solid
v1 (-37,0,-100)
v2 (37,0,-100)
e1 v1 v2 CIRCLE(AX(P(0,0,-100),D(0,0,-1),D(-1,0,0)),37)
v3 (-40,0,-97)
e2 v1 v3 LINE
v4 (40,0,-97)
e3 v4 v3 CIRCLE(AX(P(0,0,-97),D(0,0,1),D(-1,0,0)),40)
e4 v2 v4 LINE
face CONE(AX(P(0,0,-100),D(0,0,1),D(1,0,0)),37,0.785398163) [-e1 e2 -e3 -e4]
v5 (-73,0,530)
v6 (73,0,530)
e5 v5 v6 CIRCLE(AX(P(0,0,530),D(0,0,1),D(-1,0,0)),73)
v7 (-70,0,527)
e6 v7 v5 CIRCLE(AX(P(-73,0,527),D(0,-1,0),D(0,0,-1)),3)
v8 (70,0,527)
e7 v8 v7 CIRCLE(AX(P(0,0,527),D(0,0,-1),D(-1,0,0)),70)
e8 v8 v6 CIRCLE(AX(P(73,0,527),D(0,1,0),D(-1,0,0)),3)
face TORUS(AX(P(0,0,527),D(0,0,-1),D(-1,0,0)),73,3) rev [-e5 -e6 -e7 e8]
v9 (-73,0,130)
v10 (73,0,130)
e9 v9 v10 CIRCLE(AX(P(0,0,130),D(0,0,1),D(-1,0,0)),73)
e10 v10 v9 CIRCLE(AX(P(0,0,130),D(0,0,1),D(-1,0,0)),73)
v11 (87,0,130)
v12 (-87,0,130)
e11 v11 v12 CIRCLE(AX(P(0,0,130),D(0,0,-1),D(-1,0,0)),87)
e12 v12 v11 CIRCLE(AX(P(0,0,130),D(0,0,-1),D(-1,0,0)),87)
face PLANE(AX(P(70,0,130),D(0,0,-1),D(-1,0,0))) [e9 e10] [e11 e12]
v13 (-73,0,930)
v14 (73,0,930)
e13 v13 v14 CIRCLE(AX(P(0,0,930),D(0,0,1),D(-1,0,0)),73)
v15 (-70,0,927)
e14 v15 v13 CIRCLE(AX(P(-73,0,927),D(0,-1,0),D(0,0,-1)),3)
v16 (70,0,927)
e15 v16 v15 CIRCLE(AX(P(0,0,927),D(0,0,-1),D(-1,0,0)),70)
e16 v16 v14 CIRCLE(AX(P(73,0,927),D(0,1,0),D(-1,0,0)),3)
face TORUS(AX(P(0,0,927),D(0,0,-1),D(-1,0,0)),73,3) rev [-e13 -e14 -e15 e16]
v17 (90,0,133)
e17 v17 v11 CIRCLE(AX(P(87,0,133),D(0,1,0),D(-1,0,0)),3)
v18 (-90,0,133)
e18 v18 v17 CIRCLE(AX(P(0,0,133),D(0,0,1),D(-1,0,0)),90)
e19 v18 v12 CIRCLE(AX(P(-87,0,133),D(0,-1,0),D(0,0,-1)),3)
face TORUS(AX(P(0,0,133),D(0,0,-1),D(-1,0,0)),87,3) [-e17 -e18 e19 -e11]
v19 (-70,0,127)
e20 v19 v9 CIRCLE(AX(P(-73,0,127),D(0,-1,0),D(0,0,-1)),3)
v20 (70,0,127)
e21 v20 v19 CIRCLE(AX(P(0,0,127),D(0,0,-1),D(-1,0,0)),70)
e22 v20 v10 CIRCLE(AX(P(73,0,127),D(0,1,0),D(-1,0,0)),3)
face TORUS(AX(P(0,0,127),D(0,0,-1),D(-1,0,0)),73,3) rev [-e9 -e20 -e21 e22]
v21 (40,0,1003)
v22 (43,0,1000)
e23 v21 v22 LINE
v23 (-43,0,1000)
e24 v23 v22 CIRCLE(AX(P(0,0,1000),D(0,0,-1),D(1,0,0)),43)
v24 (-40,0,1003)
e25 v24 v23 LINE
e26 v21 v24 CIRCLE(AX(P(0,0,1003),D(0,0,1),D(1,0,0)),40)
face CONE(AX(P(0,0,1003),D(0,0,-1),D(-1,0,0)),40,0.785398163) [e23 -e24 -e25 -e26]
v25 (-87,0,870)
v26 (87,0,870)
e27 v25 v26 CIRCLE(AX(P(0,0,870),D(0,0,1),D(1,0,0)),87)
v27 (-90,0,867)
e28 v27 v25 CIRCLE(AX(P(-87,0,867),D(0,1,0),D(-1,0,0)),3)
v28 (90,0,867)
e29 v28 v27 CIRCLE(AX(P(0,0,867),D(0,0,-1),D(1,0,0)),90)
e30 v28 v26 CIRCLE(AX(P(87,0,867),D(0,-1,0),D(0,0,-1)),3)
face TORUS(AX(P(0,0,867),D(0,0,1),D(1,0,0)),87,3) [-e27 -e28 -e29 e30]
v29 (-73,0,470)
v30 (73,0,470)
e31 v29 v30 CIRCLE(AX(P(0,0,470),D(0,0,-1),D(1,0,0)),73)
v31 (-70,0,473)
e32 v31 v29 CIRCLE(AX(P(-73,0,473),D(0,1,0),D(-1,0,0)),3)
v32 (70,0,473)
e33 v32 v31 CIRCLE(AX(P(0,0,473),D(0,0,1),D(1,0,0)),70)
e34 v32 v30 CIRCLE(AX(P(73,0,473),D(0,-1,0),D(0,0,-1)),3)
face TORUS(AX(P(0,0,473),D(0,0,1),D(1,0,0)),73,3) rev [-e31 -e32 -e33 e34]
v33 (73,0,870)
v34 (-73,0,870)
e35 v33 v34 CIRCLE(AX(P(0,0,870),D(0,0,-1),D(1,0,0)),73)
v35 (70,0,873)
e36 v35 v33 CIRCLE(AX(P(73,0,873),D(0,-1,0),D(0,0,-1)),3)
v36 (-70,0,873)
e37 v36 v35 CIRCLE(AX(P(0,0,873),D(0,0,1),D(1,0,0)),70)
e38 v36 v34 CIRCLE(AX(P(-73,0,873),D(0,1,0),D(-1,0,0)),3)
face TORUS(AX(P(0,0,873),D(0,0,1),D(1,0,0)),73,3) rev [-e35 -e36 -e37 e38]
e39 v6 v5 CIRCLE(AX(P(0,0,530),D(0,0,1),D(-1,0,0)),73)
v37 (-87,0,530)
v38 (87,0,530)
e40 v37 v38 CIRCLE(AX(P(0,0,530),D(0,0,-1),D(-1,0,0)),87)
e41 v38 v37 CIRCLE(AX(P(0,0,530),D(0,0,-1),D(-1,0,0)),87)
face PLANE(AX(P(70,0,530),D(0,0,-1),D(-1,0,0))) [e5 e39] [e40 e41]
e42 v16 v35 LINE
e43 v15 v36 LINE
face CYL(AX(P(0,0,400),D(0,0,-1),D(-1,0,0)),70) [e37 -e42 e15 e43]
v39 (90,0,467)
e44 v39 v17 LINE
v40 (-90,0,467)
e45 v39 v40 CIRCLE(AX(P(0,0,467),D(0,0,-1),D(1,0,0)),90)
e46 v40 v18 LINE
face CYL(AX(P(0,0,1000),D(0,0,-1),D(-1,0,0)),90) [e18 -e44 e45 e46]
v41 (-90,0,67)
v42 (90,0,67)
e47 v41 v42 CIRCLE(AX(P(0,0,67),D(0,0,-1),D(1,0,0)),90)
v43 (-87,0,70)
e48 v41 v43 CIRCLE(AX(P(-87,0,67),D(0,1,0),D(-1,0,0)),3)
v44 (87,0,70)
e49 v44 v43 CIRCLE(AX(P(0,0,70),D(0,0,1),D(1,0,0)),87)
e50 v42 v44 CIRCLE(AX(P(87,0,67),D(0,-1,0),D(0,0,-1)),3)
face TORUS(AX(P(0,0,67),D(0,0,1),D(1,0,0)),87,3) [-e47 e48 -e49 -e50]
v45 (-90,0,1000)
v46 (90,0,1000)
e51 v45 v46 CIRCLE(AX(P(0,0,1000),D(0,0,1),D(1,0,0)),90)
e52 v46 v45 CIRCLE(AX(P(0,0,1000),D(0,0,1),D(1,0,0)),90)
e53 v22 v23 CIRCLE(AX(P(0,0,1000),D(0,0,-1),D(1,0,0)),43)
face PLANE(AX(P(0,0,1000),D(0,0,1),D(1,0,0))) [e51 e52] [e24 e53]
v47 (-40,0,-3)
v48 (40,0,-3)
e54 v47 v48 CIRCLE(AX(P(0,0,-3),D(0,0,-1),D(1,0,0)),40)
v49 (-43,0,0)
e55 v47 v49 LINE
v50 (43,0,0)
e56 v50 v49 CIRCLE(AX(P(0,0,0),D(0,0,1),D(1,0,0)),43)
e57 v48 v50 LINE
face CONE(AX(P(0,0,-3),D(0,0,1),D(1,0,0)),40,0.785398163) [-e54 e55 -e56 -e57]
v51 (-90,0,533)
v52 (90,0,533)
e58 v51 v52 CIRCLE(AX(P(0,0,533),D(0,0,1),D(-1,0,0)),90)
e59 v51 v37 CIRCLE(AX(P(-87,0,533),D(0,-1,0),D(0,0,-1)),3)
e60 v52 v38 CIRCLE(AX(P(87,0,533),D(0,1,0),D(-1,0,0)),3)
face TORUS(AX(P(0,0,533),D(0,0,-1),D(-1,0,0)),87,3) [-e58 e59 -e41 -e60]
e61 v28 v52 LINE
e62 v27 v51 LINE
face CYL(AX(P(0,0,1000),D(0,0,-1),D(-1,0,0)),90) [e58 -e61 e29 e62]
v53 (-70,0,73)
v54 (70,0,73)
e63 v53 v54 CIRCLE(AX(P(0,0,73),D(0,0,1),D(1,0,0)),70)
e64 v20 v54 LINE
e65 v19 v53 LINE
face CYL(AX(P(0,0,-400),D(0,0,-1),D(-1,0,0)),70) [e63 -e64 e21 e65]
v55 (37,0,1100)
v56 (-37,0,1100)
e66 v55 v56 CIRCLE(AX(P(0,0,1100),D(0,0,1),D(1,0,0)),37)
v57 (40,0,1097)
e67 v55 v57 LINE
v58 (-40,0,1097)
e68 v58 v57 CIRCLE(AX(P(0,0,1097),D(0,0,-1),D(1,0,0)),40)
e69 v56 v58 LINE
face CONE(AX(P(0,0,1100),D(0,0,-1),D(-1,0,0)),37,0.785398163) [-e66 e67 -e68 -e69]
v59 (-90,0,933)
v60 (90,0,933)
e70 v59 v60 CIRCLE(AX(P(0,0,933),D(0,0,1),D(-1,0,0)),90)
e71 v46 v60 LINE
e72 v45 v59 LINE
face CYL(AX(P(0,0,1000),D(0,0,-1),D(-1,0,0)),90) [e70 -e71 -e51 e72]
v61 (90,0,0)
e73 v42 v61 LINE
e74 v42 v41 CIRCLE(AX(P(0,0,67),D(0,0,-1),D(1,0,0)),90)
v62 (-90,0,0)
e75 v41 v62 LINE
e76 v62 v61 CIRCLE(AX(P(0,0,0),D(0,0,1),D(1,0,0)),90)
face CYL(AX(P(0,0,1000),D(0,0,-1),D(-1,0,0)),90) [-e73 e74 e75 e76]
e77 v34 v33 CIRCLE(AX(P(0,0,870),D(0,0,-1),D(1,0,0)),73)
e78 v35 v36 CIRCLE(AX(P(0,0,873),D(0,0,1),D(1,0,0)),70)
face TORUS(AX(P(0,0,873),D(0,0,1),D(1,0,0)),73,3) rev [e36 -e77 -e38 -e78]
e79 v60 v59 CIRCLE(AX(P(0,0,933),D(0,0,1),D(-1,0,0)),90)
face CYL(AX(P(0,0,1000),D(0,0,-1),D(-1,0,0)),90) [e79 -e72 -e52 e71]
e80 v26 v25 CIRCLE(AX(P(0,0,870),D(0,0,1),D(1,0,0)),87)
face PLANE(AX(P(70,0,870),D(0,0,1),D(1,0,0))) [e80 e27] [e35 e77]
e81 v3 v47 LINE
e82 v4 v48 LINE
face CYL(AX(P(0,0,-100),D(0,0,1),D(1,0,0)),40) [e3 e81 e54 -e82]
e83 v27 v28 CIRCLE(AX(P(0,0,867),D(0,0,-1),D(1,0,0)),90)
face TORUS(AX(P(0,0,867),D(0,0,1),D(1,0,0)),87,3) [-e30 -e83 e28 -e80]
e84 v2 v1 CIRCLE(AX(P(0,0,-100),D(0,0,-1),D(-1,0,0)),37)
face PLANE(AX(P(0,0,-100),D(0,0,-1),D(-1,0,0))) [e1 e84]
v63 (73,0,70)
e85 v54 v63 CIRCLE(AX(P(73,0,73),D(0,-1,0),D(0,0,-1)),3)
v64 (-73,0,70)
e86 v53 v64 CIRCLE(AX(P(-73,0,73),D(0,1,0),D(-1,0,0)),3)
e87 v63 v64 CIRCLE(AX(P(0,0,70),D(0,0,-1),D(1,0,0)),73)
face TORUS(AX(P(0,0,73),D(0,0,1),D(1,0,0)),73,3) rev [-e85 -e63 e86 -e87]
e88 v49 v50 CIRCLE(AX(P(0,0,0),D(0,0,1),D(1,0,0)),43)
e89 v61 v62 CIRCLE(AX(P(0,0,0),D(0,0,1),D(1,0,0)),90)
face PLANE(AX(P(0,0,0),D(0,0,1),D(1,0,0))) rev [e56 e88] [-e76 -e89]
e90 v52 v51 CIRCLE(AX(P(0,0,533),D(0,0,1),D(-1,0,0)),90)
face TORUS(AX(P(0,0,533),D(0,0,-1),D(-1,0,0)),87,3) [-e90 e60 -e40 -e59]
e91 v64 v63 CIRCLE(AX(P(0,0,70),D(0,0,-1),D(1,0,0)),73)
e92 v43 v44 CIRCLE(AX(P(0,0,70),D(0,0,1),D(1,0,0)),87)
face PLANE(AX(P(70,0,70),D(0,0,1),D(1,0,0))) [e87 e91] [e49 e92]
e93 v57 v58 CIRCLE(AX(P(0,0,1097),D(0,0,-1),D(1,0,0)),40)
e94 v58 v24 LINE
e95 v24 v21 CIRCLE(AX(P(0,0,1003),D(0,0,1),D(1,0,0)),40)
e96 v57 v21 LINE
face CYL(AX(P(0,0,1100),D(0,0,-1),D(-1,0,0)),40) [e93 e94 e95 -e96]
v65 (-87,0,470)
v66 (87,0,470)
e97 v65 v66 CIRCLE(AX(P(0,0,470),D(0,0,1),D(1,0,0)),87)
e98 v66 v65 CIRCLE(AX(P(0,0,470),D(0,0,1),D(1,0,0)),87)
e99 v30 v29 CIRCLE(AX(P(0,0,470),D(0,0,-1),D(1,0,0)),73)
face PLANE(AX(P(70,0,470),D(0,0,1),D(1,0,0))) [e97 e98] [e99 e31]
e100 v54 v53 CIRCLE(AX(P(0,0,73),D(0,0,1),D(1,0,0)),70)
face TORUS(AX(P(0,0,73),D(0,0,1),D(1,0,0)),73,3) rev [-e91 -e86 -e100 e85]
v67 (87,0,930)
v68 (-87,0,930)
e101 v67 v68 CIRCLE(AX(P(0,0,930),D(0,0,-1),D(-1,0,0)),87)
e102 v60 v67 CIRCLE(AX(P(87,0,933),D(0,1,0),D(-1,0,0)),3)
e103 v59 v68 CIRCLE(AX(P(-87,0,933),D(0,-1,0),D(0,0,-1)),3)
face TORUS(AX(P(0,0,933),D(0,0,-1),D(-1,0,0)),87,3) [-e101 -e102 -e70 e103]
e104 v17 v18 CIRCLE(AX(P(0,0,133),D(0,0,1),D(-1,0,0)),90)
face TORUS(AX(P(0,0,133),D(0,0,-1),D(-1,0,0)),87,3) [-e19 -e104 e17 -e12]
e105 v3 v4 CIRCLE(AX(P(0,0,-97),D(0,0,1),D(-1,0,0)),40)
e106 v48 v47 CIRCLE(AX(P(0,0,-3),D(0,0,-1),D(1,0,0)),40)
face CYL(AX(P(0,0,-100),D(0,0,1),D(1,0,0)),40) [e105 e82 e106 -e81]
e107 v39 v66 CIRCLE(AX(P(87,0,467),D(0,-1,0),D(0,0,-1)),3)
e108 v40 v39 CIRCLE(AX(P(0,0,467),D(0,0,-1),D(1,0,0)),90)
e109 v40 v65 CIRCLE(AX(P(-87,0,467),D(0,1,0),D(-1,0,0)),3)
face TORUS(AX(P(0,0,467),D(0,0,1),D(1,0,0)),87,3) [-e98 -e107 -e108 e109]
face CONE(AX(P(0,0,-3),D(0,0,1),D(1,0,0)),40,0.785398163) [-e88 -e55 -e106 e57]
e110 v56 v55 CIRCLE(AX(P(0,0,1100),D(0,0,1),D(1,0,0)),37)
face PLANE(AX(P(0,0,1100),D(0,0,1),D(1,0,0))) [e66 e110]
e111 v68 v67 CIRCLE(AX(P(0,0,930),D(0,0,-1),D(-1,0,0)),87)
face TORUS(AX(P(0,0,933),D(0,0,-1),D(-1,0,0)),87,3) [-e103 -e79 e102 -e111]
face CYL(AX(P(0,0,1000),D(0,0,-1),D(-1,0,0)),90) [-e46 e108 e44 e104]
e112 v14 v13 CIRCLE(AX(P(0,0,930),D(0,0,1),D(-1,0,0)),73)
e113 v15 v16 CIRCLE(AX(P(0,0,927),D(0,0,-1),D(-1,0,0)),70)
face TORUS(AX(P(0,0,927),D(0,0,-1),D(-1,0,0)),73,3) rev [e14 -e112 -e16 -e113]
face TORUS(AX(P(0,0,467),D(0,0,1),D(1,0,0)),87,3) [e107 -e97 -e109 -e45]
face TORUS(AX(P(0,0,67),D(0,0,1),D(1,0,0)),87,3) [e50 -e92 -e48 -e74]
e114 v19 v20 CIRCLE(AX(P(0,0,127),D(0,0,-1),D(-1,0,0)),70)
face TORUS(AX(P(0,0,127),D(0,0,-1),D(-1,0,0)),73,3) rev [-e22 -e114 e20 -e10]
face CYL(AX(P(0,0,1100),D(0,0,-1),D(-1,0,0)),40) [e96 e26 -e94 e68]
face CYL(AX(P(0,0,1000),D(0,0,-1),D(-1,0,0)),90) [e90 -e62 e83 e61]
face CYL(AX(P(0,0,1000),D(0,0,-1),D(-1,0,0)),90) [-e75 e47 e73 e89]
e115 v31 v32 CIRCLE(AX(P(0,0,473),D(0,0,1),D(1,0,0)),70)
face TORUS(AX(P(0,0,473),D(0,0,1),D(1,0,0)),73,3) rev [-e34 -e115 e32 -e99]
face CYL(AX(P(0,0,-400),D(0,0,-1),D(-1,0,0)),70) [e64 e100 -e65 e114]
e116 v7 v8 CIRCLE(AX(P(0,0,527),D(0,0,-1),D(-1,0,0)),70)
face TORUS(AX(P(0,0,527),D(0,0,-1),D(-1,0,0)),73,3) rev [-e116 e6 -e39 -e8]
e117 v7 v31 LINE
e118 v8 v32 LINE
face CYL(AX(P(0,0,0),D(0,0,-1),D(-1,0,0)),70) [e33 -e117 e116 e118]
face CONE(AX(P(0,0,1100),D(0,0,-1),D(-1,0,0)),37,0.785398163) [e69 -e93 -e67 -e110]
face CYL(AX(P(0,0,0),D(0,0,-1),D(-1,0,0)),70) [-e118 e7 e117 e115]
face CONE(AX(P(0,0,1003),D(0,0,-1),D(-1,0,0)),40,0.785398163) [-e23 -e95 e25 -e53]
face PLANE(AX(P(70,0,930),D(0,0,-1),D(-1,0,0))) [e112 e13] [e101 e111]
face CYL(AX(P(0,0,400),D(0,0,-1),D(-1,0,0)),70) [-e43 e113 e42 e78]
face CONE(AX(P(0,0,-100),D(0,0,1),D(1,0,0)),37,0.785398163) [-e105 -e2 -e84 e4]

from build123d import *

# Parameters (mm, degrees)
SKETCH1_R                  = 90
BOSS_EXTRUDE1_DEPTH        = 1000
SKETCH2_W                  = 40
SKETCH2_H                  = 60
FILLET1_R                  = 3
LPATTERN1_COUNT            = 2
LPATTERN1_PITCH            = 400
FILLET1_OF_LPATTERN1_R     = 3
LPATTERN1_COL_COUNT        = 2
LPATTERN1_COL_PITCH        = 400
FILLET1_OF_LPATTERN1_COL_R = 3
SKETCH3_R                  = 40
BOSS_EXTRUDE2_DEPTH        = 100
CHAMFER1_SIZE              = 3
BOSS_EXTRUDE3_START        = 100
SKETCH4_R                  = 40
BOSS_EXTRUDE3_DEPTH        = 100
CHAMFER2_SIZE              = 3


with BuildPart() as part:
    # Sketch1 → Boss-Extrude1 (new body)
    with BuildSketch(Plane.XY):
        Circle(SKETCH1_R)
    extrude(amount=BOSS_EXTRUDE1_DEPTH)

    # Sketch2 → Cut-Revolve1 (revolve, cut)
    with BuildSketch(Plane(origin=(0, 0, 0), x_dir=(1, 0, 0), z_dir=(0, 1, 0)), mode=Mode.PRIVATE) as cut_revolve1_sk:
        with Locations((90, -500)):
            Rectangle(SKETCH2_W, SKETCH2_H)
    cut_revolve1 = revolve(cut_revolve1_sk.sketch.rotate(Axis((0, 0, 0), (0, 0, 1)), 180), axis=Axis((0, 0, 0), (0, 0, 1)), mode=Mode.SUBTRACT)

    # Fillet1
    fillet1_edges = [part.edges().sort_by_distance(p)[0] for p in [
        (70, 0, 530),
        (-90, 0, 530),
        (70, 0, 470),
        (-90, 0, 470),
    ]]
    fillet(fillet1_edges, radius=FILLET1_R)

    # LPattern1: Cut-Revolve1 ×2
    with Locations(*[(0, 0, -i * LPATTERN1_PITCH) for i in range(1, LPATTERN1_COUNT)]):
        add(cut_revolve1, mode=Mode.SUBTRACT)

    # Fillet1 of LPattern1
    fillet1_of_lpattern1_edges = [part.edges().sort_by_distance(p)[0] for p in [
        (70, 0, 130),
        (-90, 0, 130),
        (70, 0, 70),
        (-90, 0, 70),
    ]]
    fillet(fillet1_of_lpattern1_edges, radius=FILLET1_OF_LPATTERN1_R)

    # LPattern1 col: Cut-Revolve1 ×2
    with Locations(*[(0, 0, i * LPATTERN1_COL_PITCH) for i in range(1, LPATTERN1_COL_COUNT)]):
        add(cut_revolve1, mode=Mode.SUBTRACT)

    # Fillet1 of LPattern1 col
    fillet1_of_lpattern1_col_edges = [part.edges().sort_by_distance(p)[0] for p in [
        (70, 0, 930),
        (-90, 0, 930),
        (70, 0, 870),
        (-90, 0, 870),
    ]]
    fillet(fillet1_of_lpattern1_col_edges, radius=FILLET1_OF_LPATTERN1_COL_R)

    # Sketch3 → Boss-Extrude2 (add)
    with BuildSketch(Plane.XY.offset(1000)):
        Circle(SKETCH3_R)
    extrude(amount=BOSS_EXTRUDE2_DEPTH)

    # Chamfer1
    chamfer1_edges = [part.edges().sort_by_distance(p)[0] for p in [
        (-40, 0, 1000),
        (-40, 0, 1100),
    ]]
    chamfer(chamfer1_edges, length=CHAMFER1_SIZE)

    # Sketch4 → Boss-Extrude3 (add)
    with BuildSketch(Plane(origin=(0, 0, 0), x_dir=(-1, 0, 0), z_dir=(0, 0, -1)).offset(BOSS_EXTRUDE3_START)):
        with Locations(Location((0, 0, 0), (0, 0, 180))):
            Circle(SKETCH4_R)
    extrude(amount=-BOSS_EXTRUDE3_DEPTH)

    # Chamfer2
    chamfer2_edges = [part.edges().sort_by_distance(p)[0] for p in [
        (-40, 0, 0),
        (-40, 0, -100),
    ]]
    chamfer(chamfer2_edges, length=CHAMFER2_SIZE)


solid = part.part
